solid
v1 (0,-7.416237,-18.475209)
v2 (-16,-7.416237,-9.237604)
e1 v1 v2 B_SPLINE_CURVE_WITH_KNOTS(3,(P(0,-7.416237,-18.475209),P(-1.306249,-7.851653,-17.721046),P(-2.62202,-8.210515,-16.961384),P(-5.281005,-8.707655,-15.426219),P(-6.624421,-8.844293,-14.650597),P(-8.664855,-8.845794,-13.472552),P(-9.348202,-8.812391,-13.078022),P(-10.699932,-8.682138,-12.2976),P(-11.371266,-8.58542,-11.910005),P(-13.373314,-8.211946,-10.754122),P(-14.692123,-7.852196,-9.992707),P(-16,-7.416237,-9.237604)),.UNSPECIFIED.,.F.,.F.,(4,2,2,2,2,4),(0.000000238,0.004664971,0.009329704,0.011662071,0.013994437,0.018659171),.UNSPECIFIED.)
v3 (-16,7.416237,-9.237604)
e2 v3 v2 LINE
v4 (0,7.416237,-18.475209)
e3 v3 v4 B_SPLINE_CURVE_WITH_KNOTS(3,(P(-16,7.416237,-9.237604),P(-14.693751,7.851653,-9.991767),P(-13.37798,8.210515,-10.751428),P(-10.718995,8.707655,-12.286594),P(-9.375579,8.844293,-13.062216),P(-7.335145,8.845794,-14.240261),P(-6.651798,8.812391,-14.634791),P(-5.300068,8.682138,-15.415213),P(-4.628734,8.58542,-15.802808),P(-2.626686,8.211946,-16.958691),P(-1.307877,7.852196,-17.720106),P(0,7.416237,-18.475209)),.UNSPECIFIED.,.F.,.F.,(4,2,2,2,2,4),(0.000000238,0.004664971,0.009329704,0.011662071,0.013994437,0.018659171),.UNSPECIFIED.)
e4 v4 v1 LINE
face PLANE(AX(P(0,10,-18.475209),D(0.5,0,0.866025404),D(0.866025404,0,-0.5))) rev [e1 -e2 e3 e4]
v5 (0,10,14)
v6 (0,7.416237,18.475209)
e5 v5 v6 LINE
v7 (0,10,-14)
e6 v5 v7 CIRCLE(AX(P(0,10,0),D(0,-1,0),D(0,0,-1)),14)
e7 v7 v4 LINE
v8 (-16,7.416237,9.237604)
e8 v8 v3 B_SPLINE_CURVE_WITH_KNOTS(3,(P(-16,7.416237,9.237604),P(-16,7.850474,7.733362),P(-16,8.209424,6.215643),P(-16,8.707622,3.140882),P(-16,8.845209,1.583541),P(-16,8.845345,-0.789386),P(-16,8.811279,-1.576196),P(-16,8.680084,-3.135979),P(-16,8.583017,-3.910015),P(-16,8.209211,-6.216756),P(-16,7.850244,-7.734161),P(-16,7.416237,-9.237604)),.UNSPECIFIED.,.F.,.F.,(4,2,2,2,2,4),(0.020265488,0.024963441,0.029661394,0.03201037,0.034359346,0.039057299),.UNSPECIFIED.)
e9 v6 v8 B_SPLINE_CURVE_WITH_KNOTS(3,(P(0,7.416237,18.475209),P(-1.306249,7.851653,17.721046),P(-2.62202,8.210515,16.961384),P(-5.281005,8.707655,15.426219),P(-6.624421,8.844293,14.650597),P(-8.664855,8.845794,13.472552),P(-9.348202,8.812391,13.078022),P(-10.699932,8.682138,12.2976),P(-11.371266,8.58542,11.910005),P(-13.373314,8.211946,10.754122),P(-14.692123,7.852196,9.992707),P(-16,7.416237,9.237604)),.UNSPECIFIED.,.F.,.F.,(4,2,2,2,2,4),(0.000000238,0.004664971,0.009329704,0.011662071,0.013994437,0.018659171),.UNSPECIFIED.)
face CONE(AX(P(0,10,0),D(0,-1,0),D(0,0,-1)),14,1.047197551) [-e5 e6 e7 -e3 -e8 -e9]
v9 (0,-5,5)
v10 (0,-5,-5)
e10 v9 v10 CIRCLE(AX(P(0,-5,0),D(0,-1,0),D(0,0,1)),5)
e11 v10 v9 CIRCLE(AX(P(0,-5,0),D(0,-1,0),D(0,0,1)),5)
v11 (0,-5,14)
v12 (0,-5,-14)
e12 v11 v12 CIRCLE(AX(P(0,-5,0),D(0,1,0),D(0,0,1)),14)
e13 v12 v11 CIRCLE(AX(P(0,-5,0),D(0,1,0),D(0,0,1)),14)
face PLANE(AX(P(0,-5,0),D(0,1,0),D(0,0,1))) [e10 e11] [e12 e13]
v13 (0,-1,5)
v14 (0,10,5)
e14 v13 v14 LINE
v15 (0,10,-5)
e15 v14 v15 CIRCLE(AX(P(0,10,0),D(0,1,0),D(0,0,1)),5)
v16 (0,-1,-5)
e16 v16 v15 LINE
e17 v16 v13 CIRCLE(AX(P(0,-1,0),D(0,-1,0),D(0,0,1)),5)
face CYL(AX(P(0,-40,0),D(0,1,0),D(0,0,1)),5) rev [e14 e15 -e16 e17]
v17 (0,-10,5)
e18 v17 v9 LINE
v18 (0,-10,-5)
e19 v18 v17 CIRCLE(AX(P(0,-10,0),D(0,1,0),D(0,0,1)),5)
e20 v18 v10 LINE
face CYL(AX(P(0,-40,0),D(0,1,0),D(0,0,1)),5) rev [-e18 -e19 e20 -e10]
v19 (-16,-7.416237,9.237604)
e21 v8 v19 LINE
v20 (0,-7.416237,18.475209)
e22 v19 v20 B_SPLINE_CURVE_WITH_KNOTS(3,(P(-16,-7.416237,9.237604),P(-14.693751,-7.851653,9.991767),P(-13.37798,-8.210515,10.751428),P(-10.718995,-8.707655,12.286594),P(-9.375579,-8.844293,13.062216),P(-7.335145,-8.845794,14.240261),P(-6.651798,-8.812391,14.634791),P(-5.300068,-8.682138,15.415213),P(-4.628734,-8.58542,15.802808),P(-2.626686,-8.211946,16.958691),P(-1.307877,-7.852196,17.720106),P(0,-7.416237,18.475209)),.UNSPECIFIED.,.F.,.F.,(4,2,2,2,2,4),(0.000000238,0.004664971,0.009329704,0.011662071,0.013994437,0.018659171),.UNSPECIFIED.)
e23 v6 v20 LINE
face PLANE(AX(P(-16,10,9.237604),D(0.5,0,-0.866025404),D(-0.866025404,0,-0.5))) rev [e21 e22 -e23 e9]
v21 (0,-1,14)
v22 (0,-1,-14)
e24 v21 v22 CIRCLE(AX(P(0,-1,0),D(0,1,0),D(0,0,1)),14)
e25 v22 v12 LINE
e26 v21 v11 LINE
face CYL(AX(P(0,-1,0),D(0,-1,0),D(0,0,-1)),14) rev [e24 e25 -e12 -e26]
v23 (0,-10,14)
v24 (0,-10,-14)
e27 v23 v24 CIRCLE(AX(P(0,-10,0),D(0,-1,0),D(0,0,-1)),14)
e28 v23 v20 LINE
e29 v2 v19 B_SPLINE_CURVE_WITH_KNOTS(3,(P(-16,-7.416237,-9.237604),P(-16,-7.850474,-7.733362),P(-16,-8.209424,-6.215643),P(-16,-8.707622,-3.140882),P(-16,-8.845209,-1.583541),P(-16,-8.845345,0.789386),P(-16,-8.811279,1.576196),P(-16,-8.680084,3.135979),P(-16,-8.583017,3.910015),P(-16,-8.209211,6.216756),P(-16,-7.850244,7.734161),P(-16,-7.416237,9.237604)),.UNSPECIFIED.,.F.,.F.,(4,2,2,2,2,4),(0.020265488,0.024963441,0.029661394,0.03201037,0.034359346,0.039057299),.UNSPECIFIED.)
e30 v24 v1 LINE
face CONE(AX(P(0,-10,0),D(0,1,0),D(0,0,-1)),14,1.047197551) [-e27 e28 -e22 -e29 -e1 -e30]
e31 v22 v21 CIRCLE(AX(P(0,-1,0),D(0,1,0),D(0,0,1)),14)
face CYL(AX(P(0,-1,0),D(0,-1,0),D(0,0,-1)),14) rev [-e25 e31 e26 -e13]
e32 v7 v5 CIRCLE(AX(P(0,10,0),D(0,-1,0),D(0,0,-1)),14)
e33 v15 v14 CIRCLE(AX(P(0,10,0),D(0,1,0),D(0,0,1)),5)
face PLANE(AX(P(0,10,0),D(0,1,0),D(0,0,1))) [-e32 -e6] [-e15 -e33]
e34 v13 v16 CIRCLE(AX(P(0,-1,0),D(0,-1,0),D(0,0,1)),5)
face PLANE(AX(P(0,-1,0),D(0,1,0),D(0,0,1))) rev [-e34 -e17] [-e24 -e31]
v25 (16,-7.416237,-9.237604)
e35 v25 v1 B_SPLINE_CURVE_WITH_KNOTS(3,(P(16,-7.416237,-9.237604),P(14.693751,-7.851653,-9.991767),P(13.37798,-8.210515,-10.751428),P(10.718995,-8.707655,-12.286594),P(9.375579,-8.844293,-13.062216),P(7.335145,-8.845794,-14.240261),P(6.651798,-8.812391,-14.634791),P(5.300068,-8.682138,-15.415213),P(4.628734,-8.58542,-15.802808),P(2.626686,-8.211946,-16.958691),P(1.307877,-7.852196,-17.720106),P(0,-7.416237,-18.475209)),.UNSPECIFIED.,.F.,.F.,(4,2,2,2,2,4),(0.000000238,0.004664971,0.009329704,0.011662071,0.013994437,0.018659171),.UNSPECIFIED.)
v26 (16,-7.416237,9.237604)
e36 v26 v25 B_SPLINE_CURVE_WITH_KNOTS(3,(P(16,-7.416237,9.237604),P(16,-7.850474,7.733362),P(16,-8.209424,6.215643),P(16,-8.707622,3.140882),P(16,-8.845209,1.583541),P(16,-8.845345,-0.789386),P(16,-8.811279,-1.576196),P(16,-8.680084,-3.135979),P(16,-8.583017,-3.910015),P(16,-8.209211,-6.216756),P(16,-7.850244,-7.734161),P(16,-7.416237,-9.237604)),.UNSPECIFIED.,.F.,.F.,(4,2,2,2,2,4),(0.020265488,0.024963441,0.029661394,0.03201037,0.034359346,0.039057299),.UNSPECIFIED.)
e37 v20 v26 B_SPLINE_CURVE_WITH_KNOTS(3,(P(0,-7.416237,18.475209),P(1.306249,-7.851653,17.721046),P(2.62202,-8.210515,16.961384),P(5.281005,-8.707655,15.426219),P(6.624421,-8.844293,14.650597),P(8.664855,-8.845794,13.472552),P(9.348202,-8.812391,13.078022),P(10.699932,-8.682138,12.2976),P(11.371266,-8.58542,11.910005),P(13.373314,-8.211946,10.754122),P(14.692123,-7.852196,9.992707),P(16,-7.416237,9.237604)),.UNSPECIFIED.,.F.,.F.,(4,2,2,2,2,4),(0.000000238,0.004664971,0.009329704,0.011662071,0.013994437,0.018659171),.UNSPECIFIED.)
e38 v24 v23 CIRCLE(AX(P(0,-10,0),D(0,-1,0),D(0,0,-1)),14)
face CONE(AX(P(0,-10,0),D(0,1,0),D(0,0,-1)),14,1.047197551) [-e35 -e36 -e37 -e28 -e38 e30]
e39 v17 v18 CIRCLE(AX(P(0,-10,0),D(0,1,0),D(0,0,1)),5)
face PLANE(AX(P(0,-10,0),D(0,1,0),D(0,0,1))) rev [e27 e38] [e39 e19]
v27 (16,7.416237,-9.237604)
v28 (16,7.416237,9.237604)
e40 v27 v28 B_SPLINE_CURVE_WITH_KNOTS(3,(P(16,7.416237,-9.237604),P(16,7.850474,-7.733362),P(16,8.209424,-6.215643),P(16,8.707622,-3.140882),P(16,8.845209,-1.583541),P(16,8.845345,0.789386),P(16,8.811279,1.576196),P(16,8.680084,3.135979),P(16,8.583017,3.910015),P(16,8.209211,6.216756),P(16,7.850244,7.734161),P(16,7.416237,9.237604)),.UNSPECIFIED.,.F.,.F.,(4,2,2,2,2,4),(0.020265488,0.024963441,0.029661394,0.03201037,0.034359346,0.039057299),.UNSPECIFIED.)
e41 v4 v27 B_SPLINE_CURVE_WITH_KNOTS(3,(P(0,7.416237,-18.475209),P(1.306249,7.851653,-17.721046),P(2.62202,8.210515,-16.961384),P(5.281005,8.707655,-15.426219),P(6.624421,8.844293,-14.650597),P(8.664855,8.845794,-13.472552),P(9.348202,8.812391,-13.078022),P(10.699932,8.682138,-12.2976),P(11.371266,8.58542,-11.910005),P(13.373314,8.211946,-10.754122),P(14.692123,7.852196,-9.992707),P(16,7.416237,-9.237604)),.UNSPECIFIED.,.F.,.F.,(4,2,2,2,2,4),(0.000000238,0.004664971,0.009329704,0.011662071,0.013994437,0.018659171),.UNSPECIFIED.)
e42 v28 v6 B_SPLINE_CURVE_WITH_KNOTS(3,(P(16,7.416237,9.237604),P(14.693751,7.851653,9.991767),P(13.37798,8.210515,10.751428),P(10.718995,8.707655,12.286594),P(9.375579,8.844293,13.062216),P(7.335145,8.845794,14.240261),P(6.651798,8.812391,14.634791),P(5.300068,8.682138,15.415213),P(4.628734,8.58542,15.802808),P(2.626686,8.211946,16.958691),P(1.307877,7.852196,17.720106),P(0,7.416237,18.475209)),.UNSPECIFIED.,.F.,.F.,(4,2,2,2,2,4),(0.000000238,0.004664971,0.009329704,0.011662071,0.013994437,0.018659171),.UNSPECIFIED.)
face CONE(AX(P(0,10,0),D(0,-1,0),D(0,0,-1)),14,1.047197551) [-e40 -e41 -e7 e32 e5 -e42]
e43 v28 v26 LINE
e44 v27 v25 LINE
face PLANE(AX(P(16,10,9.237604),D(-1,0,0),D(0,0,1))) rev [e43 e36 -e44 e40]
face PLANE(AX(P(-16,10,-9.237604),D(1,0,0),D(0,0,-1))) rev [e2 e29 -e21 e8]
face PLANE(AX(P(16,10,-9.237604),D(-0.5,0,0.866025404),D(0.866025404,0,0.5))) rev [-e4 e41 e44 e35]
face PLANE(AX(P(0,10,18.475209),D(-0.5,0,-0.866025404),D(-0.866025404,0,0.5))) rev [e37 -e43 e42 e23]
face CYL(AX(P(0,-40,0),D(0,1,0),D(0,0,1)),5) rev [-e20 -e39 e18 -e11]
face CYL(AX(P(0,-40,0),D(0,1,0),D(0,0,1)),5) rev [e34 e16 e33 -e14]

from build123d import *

# Parameters (mm, degrees)
BOSS_EXTRUDE1_DEPTH = 10
SKETCH2_R           = 5
CUT_EXTRUDE1_DEPTH  = 50
CUT_EXTRUDE2_START  = -15
SKETCH3_R           = 14
CUT_EXTRUDE2_DEPTH  = 4


with BuildPart() as part:
    # Sketch1 → Boss-Extrude1 (new, symmetric)
    with BuildSketch(Plane(origin=(0, 0, 0), x_dir=(1, 0, 0), z_dir=(0, 1, 0))):
        Polygon((0, 18.475208614), (-16, 9.237604307), (-16, -9.237604307), (0, -18.475208614), (16, -9.237604307), (16, 9.237604307), align=None)
    extrude(amount=BOSS_EXTRUDE1_DEPTH, both=True)

    # Sketch2 → Cut-Extrude1 (cut)
    with BuildSketch(Plane(origin=(0, 10, 0), x_dir=(1, 0, 0), z_dir=(0, 1, 0))):
        with Locations(Location((0, 0, 0), (0, 0, 270))):
            Circle(SKETCH2_R)
    extrude(amount=-CUT_EXTRUDE1_DEPTH, mode=Mode.SUBTRACT)

    # Sketch3 → Cut-Extrude2 (cut)
    with BuildSketch(Plane(origin=(0, 10, 0), x_dir=(1, 0, 0), z_dir=(0, 1, 0)).offset(CUT_EXTRUDE2_START)):
        with Locations(Location((0, 0, 0), (0, 0, 270))):
            Circle(SKETCH3_R)
    extrude(amount=CUT_EXTRUDE2_DEPTH, mode=Mode.SUBTRACT)

    # Sketch4 → Cut-Revolve1 (revolve, cut)
    with BuildSketch(Plane(origin=(0, 0, 0), x_dir=(0, 0, -1), z_dir=(1, 0, 0))):
        Polygon((18.475208614, 7.416237102), (18.475208614, 10), (14, 10), align=None)
    cut_revolve1 = revolve(axis=Axis((0, 0, 0), (0, 1, 0)), mode=Mode.SUBTRACT)

    # Mirror1: Cut-Revolve1 across plane
    add(cut_revolve1.mirror(Plane.ZX), mode=Mode.SUBTRACT)


solid = part.part
